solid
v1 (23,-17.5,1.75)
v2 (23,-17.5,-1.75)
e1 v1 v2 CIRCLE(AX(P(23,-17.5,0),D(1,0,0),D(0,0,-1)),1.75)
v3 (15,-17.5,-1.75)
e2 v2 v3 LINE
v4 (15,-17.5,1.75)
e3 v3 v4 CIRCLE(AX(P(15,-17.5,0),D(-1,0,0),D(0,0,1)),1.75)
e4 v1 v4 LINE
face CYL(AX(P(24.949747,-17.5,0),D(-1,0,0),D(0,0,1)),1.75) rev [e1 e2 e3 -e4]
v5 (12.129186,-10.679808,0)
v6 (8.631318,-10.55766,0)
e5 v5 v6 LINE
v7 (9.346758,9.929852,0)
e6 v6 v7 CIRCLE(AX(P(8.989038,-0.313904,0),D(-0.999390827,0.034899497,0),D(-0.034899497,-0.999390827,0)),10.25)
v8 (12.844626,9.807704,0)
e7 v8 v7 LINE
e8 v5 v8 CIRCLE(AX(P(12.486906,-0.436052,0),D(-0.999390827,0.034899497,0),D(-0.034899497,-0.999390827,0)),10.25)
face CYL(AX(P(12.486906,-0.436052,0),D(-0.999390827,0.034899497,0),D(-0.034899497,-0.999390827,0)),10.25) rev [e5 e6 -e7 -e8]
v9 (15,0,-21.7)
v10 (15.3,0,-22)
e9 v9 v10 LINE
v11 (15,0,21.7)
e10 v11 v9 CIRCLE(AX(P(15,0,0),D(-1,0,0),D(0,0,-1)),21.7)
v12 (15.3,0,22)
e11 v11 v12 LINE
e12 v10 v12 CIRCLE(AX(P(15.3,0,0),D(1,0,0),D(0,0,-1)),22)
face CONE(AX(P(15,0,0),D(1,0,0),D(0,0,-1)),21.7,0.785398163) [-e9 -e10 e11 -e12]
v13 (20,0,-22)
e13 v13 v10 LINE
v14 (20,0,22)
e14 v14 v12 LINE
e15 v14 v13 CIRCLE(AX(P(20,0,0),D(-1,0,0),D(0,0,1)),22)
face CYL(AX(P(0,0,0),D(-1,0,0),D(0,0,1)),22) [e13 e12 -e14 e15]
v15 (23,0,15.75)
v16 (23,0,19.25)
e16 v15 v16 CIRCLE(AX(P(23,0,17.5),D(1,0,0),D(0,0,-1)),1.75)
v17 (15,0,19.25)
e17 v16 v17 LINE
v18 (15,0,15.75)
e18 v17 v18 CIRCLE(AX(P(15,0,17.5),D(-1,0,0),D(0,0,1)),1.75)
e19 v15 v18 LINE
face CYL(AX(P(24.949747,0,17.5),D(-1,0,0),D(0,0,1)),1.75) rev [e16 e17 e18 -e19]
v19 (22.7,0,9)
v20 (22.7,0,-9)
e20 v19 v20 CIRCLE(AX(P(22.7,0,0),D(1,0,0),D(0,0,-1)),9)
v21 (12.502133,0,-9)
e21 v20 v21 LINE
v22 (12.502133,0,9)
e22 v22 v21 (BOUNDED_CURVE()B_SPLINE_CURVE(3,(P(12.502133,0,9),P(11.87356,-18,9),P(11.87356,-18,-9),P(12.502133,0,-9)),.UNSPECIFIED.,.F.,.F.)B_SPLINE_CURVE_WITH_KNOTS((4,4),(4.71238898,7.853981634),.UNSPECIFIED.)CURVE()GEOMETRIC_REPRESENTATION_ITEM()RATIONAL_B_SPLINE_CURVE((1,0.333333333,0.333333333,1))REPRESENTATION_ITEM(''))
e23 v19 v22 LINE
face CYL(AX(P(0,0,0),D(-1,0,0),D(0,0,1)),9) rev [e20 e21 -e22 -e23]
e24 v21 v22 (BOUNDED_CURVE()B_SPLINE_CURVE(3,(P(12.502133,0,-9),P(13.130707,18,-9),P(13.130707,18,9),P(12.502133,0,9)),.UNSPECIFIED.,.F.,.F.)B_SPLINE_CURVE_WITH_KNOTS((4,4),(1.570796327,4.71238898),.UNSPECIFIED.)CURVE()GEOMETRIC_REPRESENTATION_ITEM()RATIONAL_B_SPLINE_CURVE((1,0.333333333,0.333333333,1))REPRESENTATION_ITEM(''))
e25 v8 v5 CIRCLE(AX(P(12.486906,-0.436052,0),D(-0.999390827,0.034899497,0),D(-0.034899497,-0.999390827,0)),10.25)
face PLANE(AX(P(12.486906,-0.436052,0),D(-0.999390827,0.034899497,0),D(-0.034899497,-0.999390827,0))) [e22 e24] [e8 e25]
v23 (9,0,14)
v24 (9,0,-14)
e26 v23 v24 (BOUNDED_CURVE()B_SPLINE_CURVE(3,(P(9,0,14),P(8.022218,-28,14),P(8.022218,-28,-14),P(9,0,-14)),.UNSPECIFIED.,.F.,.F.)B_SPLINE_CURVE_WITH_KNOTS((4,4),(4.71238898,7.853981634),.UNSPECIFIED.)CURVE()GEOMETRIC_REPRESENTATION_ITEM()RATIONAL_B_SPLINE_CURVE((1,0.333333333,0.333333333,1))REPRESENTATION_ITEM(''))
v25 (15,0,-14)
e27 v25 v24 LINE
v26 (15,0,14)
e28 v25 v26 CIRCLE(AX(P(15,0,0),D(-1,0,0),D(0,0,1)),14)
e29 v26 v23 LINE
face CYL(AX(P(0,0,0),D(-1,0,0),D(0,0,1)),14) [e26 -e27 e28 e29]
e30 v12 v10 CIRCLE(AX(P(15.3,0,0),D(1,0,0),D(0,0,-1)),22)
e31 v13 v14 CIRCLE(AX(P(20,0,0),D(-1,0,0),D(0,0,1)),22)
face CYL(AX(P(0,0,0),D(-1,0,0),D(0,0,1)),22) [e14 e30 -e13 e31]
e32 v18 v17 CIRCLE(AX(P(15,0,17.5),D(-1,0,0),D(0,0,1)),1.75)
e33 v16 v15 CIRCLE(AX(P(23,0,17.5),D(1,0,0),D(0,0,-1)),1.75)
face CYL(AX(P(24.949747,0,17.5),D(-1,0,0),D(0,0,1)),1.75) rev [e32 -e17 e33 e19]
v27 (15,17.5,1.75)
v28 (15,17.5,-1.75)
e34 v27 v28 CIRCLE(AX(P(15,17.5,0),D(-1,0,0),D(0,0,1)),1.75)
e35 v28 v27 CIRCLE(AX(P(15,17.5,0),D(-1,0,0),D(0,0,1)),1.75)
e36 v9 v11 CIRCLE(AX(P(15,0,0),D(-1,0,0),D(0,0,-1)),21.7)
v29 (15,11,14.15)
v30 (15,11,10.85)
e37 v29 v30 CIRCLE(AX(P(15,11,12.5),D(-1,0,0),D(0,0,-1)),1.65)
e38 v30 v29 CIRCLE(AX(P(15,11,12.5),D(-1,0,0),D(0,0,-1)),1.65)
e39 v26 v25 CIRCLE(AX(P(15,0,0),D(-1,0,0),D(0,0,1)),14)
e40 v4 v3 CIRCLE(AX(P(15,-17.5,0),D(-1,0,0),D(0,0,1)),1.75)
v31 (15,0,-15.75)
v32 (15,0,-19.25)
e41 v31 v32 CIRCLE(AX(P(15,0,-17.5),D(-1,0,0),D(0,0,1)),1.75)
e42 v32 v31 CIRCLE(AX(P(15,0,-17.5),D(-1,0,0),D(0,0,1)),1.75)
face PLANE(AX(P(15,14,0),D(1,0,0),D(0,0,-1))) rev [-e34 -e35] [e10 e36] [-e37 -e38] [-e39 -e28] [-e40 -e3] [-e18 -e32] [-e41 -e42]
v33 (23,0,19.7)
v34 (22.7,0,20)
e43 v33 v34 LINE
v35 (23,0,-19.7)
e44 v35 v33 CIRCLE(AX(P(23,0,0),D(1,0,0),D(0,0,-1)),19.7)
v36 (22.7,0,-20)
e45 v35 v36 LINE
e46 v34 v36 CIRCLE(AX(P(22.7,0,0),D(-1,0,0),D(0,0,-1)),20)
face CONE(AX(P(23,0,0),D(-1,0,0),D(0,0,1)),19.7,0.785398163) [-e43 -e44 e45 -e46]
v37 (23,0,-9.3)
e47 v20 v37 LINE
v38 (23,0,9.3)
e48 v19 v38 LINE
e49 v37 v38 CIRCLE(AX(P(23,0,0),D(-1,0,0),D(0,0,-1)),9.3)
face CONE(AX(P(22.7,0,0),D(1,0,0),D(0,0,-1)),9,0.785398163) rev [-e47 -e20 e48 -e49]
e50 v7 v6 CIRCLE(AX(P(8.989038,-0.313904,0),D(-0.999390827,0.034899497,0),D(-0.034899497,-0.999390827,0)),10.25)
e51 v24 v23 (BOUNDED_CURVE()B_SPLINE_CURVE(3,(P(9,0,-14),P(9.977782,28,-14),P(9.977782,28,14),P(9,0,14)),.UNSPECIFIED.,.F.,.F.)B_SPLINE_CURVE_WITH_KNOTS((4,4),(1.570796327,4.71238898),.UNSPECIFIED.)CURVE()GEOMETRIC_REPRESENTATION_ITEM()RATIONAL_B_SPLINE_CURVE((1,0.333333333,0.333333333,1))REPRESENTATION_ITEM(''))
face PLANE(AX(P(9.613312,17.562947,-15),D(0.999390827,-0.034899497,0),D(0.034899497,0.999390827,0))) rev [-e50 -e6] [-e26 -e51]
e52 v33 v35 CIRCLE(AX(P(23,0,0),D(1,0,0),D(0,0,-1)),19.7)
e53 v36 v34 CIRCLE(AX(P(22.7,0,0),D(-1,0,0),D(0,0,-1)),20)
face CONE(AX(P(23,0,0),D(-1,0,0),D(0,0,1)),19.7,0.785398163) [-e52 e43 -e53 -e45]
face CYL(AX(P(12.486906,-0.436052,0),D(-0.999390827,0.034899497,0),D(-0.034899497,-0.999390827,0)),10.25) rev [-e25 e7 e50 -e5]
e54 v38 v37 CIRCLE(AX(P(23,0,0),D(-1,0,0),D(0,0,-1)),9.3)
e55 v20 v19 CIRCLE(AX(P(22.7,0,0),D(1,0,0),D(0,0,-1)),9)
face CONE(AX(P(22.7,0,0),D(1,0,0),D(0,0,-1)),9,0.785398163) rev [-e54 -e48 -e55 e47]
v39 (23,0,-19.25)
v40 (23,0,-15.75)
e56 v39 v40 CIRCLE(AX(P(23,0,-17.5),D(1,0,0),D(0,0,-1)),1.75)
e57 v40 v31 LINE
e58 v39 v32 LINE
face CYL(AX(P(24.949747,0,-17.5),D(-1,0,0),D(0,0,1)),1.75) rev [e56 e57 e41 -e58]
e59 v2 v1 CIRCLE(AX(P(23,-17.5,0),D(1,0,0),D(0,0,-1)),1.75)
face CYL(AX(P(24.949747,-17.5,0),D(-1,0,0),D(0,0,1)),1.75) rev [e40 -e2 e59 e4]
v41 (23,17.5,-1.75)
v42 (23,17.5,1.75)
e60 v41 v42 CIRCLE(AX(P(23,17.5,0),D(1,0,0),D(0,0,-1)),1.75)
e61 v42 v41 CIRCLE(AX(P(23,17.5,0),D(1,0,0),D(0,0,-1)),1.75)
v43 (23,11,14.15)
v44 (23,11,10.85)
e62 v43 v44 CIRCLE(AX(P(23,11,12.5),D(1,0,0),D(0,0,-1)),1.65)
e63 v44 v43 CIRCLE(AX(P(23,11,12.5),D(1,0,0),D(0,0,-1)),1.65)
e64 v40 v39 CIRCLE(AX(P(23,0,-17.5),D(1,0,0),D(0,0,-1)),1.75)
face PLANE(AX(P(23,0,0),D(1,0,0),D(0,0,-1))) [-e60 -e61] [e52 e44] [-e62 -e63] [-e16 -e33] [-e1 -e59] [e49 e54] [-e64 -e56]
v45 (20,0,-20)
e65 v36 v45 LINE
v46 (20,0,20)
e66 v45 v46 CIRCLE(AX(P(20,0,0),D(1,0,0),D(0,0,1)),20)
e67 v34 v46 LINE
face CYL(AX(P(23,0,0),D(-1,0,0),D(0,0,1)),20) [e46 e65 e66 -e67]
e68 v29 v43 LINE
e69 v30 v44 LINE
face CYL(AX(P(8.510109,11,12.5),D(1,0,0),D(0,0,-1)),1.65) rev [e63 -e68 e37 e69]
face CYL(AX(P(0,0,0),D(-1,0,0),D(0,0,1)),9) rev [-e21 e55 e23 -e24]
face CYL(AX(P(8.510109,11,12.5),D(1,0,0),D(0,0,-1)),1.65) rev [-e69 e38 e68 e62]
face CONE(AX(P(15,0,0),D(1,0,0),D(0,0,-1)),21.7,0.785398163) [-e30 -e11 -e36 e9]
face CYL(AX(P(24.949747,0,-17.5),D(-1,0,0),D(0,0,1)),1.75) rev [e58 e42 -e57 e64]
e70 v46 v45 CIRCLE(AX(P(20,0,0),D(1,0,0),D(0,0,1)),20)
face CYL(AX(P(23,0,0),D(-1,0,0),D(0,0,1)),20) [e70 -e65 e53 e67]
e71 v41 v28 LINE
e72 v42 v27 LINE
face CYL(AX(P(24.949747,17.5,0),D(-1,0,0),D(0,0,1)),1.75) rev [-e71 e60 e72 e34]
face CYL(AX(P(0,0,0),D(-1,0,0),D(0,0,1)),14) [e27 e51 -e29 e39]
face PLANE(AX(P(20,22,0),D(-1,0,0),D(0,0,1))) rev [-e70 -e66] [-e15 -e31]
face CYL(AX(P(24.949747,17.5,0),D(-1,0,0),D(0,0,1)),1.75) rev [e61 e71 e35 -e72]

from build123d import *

# Parameters (mm, degrees)
CUT_EXTRUDE1_DEPTH  = 15
SKETCH4_R           = 10.25
CUT_EXTRUDE2_DEPTH  = 3.5
SKETCH5_R           = 1.75
CUT_EXTRUDE3_DEPTH  = 5
SKETCH7_R           = 20
SKETCH7_R_2         = 1.75
SKETCH7_R_3         = 9
BOSS_EXTRUDE1_DEPTH = 3
CUT_EXTRUDE5_REACH  = 36.321
SKETCH10_R          = 1.65
CHAMFER1_SIZE       = 0.3
CHAMFER2_SIZE       = 0.3


with BuildPart() as part:
    # Sketch1 → Revolve1 (revolve)
    with BuildSketch(Plane.XY, mode=Mode.PRIVATE) as revolve1_sk:
        Polygon((0, 9), (0, 14), (15, 14), (15, 22), (20, 22), (20, 9), align=None)
    revolve(revolve1_sk.sketch.rotate(Axis((0, 0, 0), (1, 0, 0)), 90), axis=Axis((0, 0, 0), (1, 0, 0)))

    # Sketch3 → Cut-Extrude1 (cut, symmetric)
    with BuildSketch(Plane.XY):
        Polygon((9.613311632, 17.562947239), (8.386688368, -17.562947239), (-5.415654366, -17.562947239), (-5.415654366, 17.562947239), align=None)
    extrude(amount=CUT_EXTRUDE1_DEPTH, both=True, mode=Mode.SUBTRACT)

    # Sketch4 → Cut-Extrude2 (cut)
    with BuildSketch(Plane(origin=(8.989038226, -0.313904132, 0), x_dir=(0, 0, 1), z_dir=(-0.9993908270190958, 0.03489949670250087, 0))):
        with Locations(Location((0, 0, 0), (0, 0, 270))):
            Circle(SKETCH4_R)
    extrude(amount=-CUT_EXTRUDE2_DEPTH, mode=Mode.SUBTRACT)

    # Sketch5 → Cut-Extrude3 (cut)
    with BuildSketch(Plane.ZY.offset(-15)):
        with Locations((-17.5, 0)):
            Circle(SKETCH5_R)
        with Locations((0, 17.5)):
            Circle(SKETCH5_R)
        with Locations((17.5, 0)):
            Circle(SKETCH5_R)
        with Locations((0, -17.5)):
            Circle(SKETCH5_R)
    extrude(amount=-CUT_EXTRUDE3_DEPTH, mode=Mode.SUBTRACT)

    # Sketch7 → Boss-Extrude1 (add)
    with BuildSketch(Plane(origin=(20, 0, 0), x_dir=(0, 0, -1), z_dir=(1, 0, 0))):
        with Locations(Location((0, 0, 0), (0, 0, 180))):
            Circle(SKETCH7_R)
        with Locations(Location((17.5, 0, 0), (0, 0, 180))):
            Circle(SKETCH7_R_2, mode=Mode.SUBTRACT)
        with Locations(Location((0, -17.5, 0), (0, 0, 180))):
            Circle(SKETCH7_R_2, mode=Mode.SUBTRACT)
        with Locations(Location((-17.5, 0, 0), (0, 0, 180))):
            Circle(SKETCH7_R_2, mode=Mode.SUBTRACT)
        with Locations(Location((0, 17.5, 0), (0, 0, 180))):
            Circle(SKETCH7_R_2, mode=Mode.SUBTRACT)
        with Locations(Location((0, 0, 0), (0, 0, 270))):
            Circle(SKETCH7_R_3, mode=Mode.SUBTRACT)
    extrude(amount=BOSS_EXTRUDE1_DEPTH)

    # Sketch10 → Cut-Extrude5 (cut, up to next)
    with BuildSketch(Plane(origin=(23, 0, 0), x_dir=(0, 0, -1), z_dir=(1, 0, 0)), mode=Mode.PRIVATE) as cut_extrude5_sk1:
        with Locations((-12.5, 11)):
            Circle(SKETCH10_R)
    cut_extrude5_tool1 = extrude(cut_extrude5_sk1.sketch, amount=-CUT_EXTRUDE5_REACH, mode=Mode.PRIVATE) & part.part
    add(cut_extrude5_tool1.solids().sort_by_distance((23, 11, 12.5))[0], mode=Mode.SUBTRACT)

    # Chamfer1
    chamfer1_edges = [part.edges().sort_by_distance(p)[0] for p in [
        (23, 0, -20),
        (15, 0, -22),
    ]]
    chamfer(chamfer1_edges, length=CHAMFER1_SIZE)

    # Chamfer2
    chamfer2_edges = [part.edges().sort_by_distance(p)[0] for p in [
        (23, 9, 0),
    ]]
    chamfer(chamfer2_edges, length=CHAMFER2_SIZE)


solid = part.part
